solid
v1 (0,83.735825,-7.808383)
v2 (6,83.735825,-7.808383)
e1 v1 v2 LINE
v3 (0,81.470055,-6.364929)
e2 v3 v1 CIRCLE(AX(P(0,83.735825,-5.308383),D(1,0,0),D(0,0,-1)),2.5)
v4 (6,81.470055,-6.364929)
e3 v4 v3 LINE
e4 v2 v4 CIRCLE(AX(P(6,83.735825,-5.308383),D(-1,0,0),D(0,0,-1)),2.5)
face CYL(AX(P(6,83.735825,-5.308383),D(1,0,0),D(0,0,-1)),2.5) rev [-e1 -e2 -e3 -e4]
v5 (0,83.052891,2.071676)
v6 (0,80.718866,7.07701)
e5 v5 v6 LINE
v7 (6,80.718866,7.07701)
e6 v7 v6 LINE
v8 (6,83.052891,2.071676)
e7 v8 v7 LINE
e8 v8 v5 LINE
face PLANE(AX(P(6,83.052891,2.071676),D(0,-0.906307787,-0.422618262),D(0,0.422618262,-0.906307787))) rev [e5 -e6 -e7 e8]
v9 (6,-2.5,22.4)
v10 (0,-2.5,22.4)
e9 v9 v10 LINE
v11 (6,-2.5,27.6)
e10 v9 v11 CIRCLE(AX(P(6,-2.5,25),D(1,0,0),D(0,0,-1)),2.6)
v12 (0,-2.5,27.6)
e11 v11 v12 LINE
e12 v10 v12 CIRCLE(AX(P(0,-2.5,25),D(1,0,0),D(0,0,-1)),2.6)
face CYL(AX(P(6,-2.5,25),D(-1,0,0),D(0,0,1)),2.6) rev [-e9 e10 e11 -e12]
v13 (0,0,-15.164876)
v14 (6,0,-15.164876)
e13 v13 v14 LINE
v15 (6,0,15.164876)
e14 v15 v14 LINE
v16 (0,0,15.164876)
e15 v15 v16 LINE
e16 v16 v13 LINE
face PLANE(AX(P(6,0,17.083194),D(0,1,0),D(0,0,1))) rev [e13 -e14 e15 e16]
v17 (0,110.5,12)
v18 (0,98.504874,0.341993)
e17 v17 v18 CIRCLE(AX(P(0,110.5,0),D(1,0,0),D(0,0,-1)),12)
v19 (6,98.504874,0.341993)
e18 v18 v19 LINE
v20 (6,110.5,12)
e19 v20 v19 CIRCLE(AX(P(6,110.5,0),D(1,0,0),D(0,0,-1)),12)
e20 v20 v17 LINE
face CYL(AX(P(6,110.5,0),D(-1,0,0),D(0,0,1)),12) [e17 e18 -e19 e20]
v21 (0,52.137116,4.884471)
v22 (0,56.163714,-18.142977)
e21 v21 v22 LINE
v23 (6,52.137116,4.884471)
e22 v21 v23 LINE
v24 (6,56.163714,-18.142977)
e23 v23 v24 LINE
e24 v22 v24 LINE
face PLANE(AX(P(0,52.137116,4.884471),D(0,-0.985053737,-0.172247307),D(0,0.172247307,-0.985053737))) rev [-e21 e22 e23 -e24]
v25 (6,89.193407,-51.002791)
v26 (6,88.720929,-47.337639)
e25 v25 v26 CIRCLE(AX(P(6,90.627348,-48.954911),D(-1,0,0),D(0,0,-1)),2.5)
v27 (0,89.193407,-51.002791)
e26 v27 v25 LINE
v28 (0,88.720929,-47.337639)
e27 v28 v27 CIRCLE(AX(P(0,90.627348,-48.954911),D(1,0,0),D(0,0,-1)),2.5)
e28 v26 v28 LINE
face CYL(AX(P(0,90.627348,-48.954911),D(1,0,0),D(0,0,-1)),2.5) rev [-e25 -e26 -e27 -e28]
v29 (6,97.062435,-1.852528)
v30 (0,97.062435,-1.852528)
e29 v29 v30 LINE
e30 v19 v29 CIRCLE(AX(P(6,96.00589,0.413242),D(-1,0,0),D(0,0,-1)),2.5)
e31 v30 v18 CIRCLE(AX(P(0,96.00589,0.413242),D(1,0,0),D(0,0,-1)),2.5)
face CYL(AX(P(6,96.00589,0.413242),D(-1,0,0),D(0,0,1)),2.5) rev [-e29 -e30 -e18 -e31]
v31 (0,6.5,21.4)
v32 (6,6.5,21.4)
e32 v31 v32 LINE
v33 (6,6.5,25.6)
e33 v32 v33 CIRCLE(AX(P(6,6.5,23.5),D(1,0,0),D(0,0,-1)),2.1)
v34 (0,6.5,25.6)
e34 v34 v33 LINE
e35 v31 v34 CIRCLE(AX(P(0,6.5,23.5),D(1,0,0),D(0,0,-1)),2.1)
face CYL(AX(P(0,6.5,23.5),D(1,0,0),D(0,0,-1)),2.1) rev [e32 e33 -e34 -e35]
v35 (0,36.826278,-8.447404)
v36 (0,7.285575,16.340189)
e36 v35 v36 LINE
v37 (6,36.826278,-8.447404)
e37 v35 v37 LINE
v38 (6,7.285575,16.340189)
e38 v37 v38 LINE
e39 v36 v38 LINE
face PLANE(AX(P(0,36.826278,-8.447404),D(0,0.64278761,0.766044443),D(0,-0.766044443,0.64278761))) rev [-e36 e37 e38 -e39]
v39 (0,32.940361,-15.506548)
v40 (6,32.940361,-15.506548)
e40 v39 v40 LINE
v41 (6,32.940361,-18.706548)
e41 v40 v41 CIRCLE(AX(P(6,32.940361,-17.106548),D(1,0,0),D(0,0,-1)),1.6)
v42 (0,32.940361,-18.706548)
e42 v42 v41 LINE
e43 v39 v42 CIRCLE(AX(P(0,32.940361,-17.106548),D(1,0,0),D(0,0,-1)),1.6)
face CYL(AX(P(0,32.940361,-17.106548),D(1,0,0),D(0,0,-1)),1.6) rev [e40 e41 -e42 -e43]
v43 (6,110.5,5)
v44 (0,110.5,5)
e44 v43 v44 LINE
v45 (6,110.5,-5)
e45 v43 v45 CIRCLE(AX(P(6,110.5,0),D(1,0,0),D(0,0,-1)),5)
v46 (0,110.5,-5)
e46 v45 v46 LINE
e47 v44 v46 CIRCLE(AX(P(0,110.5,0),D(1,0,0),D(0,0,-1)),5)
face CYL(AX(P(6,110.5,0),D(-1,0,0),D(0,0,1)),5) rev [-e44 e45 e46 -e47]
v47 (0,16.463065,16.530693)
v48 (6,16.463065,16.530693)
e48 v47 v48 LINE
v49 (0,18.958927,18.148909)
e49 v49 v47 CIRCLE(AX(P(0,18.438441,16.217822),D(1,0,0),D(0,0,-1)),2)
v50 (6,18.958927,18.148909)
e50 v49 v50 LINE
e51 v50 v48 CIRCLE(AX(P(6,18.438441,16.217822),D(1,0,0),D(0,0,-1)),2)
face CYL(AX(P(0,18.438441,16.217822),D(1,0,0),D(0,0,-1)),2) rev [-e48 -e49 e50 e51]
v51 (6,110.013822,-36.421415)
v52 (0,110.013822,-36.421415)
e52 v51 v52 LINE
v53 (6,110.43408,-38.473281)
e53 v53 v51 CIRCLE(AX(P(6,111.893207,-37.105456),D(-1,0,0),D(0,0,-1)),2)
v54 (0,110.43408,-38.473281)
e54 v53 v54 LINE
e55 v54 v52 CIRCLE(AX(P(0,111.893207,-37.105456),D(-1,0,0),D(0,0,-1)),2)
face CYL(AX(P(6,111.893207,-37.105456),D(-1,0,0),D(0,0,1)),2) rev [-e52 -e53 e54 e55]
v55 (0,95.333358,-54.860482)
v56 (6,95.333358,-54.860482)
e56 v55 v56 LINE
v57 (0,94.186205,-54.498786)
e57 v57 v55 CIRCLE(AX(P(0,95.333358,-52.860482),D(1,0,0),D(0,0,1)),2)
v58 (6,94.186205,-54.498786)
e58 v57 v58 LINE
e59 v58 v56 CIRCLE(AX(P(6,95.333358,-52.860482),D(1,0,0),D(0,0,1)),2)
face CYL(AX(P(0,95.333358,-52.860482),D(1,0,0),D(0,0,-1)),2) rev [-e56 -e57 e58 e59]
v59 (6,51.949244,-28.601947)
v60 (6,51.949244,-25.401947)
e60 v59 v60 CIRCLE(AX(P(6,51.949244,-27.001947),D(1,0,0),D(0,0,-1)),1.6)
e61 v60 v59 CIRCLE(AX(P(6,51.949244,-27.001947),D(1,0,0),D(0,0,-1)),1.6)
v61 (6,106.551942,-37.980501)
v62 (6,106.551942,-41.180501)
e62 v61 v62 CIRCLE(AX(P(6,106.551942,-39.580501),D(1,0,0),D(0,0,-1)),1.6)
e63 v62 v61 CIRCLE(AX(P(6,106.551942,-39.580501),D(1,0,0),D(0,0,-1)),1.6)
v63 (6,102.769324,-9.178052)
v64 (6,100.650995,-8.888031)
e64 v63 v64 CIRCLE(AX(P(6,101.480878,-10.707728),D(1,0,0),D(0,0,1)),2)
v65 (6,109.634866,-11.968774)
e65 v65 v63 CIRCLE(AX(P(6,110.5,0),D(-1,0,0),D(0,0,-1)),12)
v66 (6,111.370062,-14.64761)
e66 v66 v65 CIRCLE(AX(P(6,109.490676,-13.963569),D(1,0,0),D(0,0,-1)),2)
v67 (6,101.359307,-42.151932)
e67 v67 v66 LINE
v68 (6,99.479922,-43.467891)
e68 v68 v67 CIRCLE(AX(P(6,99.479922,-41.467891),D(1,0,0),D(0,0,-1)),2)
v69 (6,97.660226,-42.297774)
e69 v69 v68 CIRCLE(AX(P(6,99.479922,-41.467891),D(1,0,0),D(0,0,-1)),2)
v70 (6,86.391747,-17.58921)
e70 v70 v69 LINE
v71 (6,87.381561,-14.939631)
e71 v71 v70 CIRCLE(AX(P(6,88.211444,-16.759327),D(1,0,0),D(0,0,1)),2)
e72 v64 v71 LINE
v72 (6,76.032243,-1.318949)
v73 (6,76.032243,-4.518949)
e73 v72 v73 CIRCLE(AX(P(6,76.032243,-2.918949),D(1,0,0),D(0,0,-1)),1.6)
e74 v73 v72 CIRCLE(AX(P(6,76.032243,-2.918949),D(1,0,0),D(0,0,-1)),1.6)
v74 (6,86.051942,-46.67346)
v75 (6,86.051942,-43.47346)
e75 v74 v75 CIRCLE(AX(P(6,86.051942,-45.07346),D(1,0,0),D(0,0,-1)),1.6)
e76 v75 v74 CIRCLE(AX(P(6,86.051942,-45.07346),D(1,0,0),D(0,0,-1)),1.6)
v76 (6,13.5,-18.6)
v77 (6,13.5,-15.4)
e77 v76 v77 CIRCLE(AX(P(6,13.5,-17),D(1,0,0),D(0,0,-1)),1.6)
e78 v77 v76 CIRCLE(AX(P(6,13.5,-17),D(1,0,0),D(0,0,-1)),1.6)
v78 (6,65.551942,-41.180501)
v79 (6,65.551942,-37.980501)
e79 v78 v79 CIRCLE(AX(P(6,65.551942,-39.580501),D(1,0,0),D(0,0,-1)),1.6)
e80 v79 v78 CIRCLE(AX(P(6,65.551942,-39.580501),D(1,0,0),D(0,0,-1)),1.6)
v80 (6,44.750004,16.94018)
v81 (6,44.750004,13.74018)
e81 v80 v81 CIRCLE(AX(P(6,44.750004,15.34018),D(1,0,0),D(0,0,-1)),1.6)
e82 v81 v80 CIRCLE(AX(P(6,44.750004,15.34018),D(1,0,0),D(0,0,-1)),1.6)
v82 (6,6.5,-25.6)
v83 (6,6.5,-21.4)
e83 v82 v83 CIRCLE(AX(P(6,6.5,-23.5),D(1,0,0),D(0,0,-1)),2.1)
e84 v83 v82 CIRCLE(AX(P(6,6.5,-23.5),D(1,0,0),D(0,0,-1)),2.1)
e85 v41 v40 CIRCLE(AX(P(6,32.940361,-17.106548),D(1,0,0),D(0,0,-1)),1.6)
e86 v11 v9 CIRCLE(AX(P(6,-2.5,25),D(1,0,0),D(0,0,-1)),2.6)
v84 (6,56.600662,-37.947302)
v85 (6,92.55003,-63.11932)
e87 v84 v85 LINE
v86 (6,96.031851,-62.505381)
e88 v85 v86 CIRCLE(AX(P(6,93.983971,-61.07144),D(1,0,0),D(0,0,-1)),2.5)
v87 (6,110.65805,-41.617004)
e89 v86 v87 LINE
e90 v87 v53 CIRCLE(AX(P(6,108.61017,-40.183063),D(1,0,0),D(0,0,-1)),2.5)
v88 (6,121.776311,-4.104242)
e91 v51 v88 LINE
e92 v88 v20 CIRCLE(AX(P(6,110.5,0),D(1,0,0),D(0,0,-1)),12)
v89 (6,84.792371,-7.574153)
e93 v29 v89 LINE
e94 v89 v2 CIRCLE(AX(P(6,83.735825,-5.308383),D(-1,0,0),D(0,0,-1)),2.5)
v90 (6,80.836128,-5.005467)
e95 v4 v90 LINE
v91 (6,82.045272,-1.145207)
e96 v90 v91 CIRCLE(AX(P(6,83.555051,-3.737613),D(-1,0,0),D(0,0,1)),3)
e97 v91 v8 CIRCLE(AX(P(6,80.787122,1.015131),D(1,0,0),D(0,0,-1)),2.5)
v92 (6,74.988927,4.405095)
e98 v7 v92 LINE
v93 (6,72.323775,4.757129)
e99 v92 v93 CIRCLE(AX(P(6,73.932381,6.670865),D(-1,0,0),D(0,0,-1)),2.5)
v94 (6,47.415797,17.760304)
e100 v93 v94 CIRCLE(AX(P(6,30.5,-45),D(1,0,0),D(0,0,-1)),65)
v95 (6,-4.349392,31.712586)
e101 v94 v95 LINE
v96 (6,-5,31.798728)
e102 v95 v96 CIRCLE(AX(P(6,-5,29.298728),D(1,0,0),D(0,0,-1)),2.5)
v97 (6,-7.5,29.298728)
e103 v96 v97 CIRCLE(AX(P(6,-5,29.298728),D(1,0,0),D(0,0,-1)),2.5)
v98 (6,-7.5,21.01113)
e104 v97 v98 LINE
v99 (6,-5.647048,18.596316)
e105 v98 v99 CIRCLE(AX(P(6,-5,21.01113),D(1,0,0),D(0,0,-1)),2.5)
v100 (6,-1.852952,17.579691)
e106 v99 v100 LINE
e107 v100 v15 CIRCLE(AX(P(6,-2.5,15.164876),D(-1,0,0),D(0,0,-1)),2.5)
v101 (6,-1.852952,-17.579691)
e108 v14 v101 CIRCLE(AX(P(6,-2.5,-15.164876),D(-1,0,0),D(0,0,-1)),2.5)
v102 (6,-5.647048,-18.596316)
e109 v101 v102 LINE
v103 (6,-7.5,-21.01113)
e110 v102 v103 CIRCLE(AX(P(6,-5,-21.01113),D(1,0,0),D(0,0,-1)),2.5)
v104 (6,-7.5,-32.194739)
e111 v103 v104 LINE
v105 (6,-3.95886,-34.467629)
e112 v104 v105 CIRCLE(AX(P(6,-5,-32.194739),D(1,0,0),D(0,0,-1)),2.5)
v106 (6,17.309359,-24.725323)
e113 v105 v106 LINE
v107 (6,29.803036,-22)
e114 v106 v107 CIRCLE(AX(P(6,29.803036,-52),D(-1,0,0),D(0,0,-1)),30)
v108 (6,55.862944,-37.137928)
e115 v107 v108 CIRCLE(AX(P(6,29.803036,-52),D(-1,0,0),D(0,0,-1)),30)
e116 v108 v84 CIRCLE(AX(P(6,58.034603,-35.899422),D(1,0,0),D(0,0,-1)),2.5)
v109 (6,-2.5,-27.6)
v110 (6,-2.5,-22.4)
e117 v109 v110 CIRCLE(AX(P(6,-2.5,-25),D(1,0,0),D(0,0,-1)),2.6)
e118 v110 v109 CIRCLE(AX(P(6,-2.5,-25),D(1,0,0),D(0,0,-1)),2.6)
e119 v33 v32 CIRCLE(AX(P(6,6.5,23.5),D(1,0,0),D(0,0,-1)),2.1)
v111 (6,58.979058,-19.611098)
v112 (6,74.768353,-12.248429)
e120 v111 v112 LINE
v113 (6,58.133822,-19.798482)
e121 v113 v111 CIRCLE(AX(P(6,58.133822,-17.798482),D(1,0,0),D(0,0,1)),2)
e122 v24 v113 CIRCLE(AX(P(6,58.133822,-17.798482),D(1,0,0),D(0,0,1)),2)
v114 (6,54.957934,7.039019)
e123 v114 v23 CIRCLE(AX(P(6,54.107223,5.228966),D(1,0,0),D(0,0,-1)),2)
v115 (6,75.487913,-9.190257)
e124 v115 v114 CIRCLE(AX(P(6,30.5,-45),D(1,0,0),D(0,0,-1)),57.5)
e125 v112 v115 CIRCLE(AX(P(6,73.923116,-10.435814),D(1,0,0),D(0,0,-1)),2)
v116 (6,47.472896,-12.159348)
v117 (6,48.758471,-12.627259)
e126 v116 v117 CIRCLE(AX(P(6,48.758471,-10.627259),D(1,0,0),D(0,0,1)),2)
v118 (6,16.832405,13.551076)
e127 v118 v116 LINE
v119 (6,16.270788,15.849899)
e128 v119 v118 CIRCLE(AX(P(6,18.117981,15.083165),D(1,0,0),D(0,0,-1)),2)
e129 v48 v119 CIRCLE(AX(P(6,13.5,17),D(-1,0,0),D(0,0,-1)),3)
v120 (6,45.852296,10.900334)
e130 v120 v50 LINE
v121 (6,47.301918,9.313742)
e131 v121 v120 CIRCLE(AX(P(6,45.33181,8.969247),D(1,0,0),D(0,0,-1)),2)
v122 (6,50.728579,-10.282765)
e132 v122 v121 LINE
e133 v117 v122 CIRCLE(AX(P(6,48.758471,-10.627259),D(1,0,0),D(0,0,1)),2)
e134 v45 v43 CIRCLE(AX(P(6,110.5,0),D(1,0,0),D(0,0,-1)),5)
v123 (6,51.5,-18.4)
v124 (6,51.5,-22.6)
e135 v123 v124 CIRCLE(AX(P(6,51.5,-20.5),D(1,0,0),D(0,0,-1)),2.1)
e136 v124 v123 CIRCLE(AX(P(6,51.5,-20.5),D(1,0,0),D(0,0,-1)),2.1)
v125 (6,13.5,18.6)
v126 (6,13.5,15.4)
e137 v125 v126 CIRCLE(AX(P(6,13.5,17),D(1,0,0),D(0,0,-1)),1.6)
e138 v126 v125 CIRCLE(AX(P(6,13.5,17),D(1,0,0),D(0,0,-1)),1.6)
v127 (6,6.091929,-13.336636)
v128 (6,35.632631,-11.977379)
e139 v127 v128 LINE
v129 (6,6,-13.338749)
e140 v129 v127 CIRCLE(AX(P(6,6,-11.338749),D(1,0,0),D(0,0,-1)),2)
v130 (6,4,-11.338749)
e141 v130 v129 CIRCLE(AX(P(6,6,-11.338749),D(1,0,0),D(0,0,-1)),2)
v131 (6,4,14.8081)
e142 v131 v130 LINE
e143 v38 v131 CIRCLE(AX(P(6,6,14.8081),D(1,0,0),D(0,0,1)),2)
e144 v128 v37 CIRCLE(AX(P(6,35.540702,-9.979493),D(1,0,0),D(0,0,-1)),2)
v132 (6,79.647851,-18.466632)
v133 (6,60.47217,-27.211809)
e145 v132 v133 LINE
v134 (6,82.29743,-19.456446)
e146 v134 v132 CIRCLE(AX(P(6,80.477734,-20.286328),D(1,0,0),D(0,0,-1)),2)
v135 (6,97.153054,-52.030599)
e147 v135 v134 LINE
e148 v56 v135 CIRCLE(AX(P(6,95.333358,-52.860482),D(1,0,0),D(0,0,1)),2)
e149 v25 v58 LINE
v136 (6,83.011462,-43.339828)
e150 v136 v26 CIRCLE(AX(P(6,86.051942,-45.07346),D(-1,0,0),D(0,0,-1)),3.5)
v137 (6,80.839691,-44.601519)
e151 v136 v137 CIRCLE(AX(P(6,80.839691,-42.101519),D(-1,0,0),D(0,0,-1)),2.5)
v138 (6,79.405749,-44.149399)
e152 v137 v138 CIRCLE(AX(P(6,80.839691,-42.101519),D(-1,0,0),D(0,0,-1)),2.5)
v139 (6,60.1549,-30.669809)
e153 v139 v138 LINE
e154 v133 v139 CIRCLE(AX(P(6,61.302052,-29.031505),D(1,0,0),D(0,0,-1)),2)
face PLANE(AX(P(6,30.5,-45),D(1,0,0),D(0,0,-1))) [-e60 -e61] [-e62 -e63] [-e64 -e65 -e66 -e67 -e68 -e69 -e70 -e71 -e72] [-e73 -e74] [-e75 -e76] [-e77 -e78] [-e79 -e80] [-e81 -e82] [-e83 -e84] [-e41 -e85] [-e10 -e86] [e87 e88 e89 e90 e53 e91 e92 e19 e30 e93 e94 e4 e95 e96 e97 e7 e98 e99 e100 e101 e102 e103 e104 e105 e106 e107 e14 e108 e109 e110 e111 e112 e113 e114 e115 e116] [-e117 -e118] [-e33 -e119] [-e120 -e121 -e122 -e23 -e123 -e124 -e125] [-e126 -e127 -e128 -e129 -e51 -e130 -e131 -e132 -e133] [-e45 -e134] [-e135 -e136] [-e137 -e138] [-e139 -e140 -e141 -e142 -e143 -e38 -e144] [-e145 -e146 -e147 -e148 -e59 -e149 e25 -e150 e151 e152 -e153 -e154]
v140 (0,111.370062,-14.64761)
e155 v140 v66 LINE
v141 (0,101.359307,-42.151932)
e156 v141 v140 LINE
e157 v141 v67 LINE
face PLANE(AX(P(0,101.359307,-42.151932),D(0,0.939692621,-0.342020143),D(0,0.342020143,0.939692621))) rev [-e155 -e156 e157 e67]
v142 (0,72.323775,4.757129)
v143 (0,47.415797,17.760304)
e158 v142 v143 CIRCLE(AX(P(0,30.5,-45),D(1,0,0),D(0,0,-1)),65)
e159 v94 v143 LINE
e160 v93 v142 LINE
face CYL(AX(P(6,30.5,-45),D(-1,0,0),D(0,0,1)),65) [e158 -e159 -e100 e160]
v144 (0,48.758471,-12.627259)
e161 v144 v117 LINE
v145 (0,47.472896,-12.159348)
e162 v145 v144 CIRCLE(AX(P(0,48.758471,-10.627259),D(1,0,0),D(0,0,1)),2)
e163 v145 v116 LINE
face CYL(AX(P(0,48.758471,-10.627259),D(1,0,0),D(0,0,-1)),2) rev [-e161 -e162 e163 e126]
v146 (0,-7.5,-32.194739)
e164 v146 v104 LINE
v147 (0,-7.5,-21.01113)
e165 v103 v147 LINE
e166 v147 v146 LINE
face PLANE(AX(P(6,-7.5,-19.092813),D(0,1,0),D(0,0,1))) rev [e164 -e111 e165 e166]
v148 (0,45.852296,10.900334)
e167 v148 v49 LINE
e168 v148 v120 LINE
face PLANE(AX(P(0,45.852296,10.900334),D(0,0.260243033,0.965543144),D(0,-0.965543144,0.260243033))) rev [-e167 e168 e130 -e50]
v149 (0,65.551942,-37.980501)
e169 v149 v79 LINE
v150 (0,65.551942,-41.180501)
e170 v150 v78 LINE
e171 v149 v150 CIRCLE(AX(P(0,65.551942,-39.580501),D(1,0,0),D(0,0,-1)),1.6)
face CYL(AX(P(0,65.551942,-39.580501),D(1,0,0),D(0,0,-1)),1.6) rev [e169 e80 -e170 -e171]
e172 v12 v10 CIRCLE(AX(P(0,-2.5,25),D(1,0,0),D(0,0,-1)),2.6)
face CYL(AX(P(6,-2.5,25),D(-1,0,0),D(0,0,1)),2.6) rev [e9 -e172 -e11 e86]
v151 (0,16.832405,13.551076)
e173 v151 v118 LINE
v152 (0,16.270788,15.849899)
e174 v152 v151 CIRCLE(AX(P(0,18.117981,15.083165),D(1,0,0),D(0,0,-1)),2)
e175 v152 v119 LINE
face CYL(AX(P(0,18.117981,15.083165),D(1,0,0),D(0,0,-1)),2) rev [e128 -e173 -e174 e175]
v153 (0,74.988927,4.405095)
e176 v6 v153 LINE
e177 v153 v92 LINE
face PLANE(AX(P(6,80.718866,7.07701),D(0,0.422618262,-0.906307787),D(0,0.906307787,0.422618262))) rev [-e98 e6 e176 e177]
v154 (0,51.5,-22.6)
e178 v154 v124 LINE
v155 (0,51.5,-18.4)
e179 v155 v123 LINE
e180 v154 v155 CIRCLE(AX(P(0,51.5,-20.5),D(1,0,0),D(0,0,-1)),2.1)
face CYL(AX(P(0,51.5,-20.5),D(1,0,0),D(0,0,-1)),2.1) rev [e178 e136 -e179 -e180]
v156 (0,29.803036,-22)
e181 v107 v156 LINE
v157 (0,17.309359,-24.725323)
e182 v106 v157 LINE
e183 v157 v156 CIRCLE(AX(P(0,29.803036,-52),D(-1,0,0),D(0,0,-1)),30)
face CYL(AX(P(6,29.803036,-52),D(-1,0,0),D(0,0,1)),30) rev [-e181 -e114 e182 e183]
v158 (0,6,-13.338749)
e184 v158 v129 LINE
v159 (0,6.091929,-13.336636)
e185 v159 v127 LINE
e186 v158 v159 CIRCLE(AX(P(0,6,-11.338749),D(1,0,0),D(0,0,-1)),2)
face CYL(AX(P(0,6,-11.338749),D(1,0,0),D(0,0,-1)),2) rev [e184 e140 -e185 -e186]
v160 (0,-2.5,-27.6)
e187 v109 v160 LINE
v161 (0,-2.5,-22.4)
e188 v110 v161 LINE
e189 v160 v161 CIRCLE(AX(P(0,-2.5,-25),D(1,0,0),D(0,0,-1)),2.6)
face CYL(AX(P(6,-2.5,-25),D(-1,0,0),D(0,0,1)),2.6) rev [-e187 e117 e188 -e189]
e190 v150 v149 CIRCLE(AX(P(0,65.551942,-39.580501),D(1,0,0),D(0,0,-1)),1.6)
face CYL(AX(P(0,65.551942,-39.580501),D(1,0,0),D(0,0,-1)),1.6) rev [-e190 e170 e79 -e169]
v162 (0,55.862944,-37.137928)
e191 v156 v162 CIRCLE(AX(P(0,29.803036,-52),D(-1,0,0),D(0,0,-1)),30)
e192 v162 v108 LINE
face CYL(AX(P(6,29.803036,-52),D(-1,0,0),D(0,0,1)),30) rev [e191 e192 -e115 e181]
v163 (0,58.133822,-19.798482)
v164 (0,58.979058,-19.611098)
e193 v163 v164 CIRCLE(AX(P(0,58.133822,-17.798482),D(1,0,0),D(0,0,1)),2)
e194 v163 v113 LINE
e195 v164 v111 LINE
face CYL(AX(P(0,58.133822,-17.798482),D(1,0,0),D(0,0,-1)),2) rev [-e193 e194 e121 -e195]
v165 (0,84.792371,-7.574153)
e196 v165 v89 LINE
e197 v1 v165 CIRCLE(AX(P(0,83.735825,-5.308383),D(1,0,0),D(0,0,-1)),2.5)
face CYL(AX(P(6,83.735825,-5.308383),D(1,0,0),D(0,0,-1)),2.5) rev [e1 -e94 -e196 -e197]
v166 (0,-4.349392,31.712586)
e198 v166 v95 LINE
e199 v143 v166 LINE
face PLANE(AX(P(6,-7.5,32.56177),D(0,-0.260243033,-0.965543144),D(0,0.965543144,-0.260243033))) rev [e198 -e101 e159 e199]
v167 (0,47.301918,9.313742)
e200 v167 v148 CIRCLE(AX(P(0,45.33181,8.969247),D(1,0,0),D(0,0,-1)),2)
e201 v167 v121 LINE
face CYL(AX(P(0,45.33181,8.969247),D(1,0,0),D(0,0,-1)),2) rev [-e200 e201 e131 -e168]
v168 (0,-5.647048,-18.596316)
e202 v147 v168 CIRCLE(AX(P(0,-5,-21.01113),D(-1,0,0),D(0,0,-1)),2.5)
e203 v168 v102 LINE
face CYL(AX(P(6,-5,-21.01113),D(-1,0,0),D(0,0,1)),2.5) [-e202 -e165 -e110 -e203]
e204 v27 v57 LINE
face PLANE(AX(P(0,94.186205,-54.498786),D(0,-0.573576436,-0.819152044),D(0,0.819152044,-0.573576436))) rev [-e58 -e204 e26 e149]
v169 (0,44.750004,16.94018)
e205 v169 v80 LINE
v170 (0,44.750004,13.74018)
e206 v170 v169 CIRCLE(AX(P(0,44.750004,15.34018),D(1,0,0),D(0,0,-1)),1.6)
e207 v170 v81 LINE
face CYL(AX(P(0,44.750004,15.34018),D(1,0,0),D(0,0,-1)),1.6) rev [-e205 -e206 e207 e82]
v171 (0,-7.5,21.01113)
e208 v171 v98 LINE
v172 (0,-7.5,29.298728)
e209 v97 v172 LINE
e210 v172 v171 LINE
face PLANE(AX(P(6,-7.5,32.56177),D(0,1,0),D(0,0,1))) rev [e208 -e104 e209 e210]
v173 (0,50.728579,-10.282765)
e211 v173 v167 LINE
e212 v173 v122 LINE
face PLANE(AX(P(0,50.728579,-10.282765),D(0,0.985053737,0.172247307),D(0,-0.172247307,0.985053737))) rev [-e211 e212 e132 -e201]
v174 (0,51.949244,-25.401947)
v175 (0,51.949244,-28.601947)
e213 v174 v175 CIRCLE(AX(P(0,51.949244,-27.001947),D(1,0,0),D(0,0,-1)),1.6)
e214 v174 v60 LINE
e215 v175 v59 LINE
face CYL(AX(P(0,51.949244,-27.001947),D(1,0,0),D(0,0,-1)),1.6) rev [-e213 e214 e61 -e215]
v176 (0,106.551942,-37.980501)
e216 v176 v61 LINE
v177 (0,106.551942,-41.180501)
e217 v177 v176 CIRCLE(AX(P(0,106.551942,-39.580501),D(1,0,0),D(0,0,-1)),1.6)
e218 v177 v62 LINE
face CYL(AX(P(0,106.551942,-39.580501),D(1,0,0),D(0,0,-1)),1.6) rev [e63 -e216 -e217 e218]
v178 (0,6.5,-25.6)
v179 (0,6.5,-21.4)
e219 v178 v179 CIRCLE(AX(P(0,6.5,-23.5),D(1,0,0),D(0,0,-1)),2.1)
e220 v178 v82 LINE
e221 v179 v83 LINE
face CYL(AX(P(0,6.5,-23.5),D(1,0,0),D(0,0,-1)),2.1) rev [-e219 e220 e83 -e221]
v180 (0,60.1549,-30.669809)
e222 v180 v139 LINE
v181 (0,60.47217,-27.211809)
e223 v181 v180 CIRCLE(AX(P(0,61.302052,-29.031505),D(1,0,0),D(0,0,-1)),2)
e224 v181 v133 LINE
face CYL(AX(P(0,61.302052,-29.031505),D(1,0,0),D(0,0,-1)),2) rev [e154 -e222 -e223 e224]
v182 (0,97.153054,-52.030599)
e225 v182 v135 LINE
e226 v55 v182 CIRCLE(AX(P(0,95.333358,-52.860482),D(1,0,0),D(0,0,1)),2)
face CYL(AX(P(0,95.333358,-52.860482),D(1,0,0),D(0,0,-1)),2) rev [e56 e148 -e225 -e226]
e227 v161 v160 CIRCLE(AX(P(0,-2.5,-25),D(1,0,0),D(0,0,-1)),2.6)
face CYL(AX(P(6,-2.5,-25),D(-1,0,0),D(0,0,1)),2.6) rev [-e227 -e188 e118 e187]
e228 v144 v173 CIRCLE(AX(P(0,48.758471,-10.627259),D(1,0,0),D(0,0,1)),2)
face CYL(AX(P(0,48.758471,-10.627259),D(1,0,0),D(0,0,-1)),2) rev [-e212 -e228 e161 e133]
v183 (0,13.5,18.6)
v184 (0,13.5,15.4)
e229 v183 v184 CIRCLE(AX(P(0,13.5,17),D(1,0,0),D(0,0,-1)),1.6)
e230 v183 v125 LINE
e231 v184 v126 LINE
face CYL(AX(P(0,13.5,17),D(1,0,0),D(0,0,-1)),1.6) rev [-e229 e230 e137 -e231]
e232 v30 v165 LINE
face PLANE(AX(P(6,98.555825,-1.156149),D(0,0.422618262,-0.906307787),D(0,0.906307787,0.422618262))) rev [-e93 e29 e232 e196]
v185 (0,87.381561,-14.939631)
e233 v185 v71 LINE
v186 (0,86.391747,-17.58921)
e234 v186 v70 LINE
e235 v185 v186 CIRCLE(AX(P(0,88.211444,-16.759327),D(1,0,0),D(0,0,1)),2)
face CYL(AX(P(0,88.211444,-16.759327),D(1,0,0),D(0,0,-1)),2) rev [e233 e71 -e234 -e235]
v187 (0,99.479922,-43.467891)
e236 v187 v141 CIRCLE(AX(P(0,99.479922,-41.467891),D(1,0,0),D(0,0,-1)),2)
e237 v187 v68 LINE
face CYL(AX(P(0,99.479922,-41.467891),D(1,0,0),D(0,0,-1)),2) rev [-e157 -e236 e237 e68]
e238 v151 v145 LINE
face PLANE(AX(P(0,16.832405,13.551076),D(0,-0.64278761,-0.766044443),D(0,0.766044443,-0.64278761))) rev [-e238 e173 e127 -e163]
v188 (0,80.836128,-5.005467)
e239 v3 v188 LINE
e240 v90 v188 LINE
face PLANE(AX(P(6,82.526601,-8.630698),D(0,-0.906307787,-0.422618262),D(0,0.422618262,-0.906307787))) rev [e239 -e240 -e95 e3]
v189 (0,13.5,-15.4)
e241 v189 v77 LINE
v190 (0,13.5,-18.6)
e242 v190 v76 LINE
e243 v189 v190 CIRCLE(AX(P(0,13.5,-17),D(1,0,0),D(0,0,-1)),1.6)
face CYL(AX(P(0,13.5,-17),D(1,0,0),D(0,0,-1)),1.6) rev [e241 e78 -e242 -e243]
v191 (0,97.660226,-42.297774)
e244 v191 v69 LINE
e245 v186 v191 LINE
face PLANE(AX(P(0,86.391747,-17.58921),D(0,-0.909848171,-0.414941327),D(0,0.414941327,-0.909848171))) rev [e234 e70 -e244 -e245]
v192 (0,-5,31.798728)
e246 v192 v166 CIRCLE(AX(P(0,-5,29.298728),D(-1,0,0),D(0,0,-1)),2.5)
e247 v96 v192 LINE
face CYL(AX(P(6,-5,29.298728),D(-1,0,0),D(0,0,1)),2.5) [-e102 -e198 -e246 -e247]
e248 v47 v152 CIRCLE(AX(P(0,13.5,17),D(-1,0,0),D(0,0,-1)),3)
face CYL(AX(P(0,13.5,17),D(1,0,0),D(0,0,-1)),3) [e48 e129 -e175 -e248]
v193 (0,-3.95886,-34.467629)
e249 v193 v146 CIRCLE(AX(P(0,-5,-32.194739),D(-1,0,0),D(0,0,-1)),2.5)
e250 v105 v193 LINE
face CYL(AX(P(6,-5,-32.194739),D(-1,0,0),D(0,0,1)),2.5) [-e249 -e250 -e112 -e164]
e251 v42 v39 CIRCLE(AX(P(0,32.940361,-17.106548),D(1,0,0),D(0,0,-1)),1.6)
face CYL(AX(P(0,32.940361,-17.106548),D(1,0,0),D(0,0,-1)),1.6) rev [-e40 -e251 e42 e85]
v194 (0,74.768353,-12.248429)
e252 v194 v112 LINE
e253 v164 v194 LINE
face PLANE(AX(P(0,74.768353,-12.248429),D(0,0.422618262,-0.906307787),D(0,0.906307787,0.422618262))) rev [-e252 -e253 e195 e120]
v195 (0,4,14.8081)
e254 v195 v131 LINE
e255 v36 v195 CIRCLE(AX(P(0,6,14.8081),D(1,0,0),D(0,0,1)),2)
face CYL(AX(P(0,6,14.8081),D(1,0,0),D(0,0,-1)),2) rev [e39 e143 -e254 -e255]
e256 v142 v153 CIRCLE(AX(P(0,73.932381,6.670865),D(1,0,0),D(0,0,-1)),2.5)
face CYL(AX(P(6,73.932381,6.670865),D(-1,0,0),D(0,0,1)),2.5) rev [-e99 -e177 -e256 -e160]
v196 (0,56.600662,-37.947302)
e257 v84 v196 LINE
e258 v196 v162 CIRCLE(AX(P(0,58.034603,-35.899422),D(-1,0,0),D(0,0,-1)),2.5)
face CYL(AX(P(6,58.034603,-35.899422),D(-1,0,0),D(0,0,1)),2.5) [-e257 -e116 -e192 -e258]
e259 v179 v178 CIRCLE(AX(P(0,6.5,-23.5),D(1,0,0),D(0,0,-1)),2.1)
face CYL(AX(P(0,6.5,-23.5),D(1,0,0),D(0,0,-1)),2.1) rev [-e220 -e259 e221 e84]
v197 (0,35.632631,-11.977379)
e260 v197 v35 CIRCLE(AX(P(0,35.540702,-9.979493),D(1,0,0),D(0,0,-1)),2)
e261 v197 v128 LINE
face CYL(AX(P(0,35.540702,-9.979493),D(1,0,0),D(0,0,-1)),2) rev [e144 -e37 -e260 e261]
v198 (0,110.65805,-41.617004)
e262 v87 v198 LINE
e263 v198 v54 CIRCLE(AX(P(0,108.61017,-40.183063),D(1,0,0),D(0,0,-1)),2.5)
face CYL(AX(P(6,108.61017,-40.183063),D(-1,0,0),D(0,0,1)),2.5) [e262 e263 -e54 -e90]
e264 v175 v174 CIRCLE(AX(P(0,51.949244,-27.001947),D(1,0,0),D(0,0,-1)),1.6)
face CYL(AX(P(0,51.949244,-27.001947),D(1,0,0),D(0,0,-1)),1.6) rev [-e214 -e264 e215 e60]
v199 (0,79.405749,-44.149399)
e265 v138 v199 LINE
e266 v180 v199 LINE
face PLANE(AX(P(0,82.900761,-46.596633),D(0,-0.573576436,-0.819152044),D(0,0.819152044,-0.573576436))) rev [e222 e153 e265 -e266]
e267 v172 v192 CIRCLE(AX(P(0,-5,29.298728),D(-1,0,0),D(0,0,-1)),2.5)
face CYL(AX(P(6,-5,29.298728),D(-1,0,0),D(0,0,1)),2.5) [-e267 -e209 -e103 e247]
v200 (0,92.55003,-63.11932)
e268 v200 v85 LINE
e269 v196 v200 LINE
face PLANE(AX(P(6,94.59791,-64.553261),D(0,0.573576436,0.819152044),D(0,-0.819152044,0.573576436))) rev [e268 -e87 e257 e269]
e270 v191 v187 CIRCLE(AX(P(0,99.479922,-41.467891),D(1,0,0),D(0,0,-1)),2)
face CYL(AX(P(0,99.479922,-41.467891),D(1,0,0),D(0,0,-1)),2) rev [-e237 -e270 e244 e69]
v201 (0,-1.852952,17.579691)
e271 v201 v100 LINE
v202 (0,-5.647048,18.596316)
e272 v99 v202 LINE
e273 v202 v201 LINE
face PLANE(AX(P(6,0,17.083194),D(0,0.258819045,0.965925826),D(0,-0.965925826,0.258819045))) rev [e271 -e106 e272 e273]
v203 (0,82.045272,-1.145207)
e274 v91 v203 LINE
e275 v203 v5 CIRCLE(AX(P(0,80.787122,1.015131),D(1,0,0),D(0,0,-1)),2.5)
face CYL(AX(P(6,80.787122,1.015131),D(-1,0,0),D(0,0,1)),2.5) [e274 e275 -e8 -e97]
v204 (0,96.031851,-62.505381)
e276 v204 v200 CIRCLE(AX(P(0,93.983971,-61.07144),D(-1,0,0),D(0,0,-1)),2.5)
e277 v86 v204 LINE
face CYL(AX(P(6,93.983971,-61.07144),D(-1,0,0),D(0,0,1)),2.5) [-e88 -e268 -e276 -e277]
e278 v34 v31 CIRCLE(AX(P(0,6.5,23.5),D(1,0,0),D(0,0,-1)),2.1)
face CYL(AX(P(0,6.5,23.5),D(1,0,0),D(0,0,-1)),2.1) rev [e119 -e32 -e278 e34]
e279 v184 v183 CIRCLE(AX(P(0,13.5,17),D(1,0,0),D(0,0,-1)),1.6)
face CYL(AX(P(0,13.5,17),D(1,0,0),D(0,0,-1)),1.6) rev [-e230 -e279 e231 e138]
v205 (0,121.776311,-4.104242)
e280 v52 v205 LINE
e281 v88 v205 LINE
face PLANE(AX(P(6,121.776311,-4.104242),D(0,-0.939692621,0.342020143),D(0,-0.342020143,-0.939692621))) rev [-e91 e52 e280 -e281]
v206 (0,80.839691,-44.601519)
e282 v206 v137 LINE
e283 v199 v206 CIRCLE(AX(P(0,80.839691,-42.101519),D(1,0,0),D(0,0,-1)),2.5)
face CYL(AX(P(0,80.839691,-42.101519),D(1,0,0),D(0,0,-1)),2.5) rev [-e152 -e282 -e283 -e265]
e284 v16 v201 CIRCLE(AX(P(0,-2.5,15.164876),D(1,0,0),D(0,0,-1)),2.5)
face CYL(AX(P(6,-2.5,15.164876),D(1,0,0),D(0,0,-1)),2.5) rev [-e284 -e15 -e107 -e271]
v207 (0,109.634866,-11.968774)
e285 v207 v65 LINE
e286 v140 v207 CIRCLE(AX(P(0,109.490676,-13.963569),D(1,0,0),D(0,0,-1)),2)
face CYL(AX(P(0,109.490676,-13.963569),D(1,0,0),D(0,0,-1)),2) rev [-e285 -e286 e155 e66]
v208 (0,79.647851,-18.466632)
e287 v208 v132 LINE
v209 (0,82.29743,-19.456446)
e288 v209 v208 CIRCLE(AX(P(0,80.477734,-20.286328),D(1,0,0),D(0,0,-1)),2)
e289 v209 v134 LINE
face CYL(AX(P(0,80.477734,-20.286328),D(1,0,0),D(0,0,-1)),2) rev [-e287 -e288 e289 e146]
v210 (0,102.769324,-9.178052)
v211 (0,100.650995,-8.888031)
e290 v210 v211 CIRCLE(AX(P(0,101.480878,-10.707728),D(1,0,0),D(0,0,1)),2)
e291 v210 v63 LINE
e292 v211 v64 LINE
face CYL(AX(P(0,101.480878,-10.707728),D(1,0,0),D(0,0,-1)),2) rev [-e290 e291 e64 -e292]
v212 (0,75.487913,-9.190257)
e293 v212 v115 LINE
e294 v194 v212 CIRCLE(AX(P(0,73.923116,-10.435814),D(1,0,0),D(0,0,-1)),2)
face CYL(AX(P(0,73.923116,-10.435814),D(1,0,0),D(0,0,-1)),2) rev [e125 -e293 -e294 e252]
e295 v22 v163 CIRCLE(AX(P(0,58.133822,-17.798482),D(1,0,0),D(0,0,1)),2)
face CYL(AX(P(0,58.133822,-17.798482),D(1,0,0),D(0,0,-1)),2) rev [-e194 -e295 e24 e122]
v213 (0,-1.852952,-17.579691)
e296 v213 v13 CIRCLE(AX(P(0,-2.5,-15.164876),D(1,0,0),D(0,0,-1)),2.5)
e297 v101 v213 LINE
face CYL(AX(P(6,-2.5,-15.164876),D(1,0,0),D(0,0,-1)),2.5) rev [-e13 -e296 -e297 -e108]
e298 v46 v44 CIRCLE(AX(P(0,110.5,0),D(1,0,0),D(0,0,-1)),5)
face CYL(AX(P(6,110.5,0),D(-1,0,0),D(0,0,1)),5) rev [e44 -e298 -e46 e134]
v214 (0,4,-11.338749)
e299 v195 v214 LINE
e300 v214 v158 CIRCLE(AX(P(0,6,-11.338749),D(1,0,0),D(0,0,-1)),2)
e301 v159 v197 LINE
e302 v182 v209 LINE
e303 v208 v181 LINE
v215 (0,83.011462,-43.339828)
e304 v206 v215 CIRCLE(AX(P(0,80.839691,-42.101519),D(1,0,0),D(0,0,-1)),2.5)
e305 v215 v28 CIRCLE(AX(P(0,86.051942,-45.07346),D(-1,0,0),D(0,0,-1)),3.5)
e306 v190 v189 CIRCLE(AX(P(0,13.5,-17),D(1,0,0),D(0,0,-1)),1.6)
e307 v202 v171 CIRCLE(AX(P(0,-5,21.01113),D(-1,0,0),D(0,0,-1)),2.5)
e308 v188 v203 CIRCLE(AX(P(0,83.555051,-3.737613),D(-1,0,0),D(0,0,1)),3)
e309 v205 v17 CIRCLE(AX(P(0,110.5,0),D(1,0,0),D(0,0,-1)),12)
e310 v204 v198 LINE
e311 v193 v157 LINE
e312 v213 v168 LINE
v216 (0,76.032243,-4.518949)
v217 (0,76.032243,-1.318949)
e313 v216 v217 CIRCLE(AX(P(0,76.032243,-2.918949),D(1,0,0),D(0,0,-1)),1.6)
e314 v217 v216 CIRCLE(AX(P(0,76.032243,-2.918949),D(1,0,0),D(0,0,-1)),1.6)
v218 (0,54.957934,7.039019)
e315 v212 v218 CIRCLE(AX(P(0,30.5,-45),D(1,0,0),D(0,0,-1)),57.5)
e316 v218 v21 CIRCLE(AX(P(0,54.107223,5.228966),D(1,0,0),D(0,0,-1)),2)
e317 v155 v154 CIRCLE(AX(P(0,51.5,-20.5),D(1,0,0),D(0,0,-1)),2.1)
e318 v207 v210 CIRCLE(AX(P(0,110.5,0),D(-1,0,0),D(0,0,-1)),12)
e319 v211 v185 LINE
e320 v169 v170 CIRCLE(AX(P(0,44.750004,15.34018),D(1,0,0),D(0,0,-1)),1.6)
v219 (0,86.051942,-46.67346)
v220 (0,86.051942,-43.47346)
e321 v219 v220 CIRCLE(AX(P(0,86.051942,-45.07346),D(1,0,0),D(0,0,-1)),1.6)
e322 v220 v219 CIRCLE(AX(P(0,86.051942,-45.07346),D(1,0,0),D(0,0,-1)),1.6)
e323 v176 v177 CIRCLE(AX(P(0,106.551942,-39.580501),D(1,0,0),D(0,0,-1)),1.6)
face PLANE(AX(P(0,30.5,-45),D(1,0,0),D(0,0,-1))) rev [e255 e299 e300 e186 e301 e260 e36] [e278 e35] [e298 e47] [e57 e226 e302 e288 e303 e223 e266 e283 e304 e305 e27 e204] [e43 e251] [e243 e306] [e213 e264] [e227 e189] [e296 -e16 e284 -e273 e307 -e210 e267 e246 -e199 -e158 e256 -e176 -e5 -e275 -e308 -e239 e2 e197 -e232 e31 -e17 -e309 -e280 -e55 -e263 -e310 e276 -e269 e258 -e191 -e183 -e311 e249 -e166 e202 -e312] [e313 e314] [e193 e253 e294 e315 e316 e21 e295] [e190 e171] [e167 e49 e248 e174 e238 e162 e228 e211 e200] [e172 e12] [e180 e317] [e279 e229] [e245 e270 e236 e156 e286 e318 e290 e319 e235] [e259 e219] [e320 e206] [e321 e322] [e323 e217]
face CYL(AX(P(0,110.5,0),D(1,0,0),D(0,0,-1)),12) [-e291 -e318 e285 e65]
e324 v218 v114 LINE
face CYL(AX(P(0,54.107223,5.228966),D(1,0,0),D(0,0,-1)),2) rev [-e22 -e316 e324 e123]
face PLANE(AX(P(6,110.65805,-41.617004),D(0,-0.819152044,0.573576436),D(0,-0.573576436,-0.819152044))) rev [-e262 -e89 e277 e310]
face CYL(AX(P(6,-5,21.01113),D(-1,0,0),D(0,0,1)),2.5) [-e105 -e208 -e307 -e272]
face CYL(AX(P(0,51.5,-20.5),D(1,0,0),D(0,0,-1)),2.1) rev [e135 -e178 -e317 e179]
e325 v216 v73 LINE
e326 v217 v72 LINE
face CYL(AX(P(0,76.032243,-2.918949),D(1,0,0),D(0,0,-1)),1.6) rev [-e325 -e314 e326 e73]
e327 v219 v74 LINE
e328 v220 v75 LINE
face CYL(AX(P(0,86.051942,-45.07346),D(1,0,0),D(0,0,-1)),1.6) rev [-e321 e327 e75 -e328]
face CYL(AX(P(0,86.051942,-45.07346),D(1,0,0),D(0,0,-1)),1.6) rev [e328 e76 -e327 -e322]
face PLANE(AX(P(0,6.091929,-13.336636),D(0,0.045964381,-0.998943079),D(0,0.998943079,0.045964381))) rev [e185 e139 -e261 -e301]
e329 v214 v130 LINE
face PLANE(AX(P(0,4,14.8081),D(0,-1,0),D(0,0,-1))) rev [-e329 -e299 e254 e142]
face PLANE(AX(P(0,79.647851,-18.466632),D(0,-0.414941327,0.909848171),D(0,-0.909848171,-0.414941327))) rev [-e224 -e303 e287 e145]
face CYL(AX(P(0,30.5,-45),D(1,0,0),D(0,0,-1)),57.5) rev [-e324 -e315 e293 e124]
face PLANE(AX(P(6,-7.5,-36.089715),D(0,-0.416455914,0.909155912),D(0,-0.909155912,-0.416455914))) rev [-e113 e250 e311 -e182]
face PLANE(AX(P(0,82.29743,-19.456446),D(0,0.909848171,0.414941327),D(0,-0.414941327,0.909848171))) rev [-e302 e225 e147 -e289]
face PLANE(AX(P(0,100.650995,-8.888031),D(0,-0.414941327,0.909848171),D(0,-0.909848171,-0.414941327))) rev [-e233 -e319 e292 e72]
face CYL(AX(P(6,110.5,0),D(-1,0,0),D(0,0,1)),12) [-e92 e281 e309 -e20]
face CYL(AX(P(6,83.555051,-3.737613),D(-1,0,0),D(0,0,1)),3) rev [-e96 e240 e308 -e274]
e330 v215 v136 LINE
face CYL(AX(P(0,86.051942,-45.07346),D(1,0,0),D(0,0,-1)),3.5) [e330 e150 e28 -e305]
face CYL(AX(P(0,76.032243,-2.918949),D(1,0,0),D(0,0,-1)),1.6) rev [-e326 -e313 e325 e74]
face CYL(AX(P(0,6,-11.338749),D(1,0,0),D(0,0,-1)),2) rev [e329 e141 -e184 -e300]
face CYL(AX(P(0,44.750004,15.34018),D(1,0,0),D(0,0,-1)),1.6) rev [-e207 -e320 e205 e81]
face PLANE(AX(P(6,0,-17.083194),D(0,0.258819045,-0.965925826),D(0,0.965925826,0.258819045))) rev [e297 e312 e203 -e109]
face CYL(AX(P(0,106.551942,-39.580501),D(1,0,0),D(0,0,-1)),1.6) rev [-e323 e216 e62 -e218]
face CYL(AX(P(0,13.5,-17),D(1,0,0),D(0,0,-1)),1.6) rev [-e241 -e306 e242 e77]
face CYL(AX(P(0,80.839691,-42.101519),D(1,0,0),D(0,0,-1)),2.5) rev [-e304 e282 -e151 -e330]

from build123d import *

# Parameters (mm, degrees)
SKETCH_1_R          = 5
SKETCH_1_R_2        = 2.6
EXTRUDE_1_DEPTH     = 6
SKETCH_2_R          = 1.6
SKETCH_2_R_2        = 2.1
CUT_EXTRUDE_1_DEPTH = 139.597884305
CUT_EXTRUDE_2_DEPTH = 139.597884305
FILLET_R2_5_1_R     = 2.5


with BuildPart() as part:
    # 草图1 → 凸台-拉伸1 (new body)
    with BuildSketch(Plane(origin=(0, 0, 0), x_dir=(0, 0, -1), z_dir=(1, 0, 0))):
        with BuildLine():
            Line((-17.083193756, 0), (17.083193756, 0))
            Line((17.083193756, 0), (19.092812699, -7.5))
            Line((19.092812699, -7.5), (36.089714585, -7.5))
            Line((36.089714585, -7.5), (24.725322655, 17.309358564))
            ThreePointArc((24.725322655, 17.309358564), (23.529105799, 39.258626053), (37.618636127, 56.131278873))
            Line((37.618636127, 56.131278873), (64.553261218, 94.597910009))
            Line((64.553261218, 94.597910009), (41.617003978, 110.658050227))
            ThreePointArc((41.617003978, 110.658050227), (40.005403895, 111.103849583), (38.473281109, 110.434079727))
            ThreePointArc((38.473281109, 110.434079727), (37.50675935, 109.933882183), (36.421415399, 110.013822175))
            Line((36.421415399, 110.013822175), (4.10424172, 121.776311449))
            ThreePointArc((4.10424172, 121.776311449), (-11.904439355, 112.011397909), (1.156148672, 98.55582484))
            Line((1.156148672, 98.55582484), (8.630698442, 82.526601129))
            Line((8.630698442, 82.526601129), (5.005467294, 80.836128082))
            ThreePointArc((5.005467294, 80.836128082), (2.840887568, 80.692205939), (1.145207204, 82.045271746))
            ThreePointArc((1.145207204, 82.045271746), (-0.267859766, 83.172826585), (-2.071676205, 83.052891466))
            Line((-2.071676205, 83.052891466), (-7.077009672, 80.718866138))
            Line((-7.077009672, 80.718866138), (-3.722354698, 73.52478533))
            ThreePointArc((-3.722354698, 73.52478533), (-12.249590693, 61.281233983), (-17.760304381, 47.415797172))
            Line((-17.760304381, 47.415797172), (-32.561769984, -7.5))
            Line((-32.561769984, -7.5), (-19.092812699, -7.5))
            Line((-19.092812699, -7.5), (-17.083193756, 0))
        make_face()
        with Locations((0, 110.5)):
            Circle(SKETCH_1_R, mode=Mode.SUBTRACT)
        with Locations((-25, -2.5)):
            Circle(SKETCH_1_R_2, mode=Mode.SUBTRACT)
        with Locations((25, -2.5)):
            Circle(SKETCH_1_R_2, mode=Mode.SUBTRACT)
    extrude(amount=EXTRUDE_1_DEPTH)

    # 草图2 → 切除-拉伸1 (cut, through all)
    with BuildSketch(Plane(origin=(6, 0, 0), x_dir=(0, 0, -1), z_dir=(1, 0, 0))):
        with Locations((-17, 13.5)):
            Circle(SKETCH_2_R)
        with Locations((17, 13.5)):
            Circle(SKETCH_2_R)
        with Locations((39.580501258, 106.551942354)):
            Circle(SKETCH_2_R)
        with Locations((45.073459702, 86.051942354)):
            Circle(SKETCH_2_R)
        with Locations((39.580501258, 65.551942354)):
            Circle(SKETCH_2_R)
        with Locations((27.001946929, 51.949244407)):
            Circle(SKETCH_2_R)
        with Locations((17.106548453, 32.940360797)):
            Circle(SKETCH_2_R)
        with Locations((2.918948689, 76.032242648)):
            Circle(SKETCH_2_R)
        with Locations((-15.340180452, 44.750004318)):
            Circle(SKETCH_2_R)
        with Locations((-23.5, 6.5)):
            Circle(SKETCH_2_R_2)
        with Locations((23.5, 6.5)):
            Circle(SKETCH_2_R_2)
        with Locations((20.5, 51.5)):
            Circle(SKETCH_2_R_2)
    extrude(amount=-CUT_EXTRUDE_1_DEPTH, mode=Mode.SUBTRACT)

    # 草图3 → 切除-拉伸2 (cut, through all)
    with BuildSketch(Plane(origin=(6, 0, 0), x_dir=(0, 0, -1), z_dir=(1, 0, 0))):
        with BuildLine():
            Line((12.248429119, 74.768352656), (19.611098021, 58.979058243))
            ThreePointArc((19.611098021, 58.979058243), (19.571846918, 57.209063128), (18.142977061, 56.163714245))
            Line((18.142977061, 56.163714245), (-4.884471281, 52.137115682))
            ThreePointArc((-4.884471281, 52.137115682), (-6.818374298, 52.893229365), (-7.039018719, 54.957933901))
            ThreePointArc((-7.039018719, 54.957933901), (-0.107884381, 66.158502025), (9.190257276, 75.487913111))
            ThreePointArc((9.190257276, 75.487913111), (10.893886548, 75.869951802), (12.248429119, 74.768352656))
        make_face()
        with BuildLine():
            Line((8.888031445, 100.650995125), (14.939630847, 87.381560906))
            ThreePointArc((14.939630847, 87.381560906), (16.059423219, 86.337908285), (17.589209845, 86.391747219))
            Line((17.589209845, 86.391747219), (42.297774007, 97.660225561))
            ThreePointArc((42.297774007, 97.660225561), (43.466338702, 99.558713974), (42.151931639, 101.359307145))
            Line((42.151931639, 101.359307145), (14.64760953, 111.370061707))
            ThreePointArc((14.64760953, 111.370061707), (12.876257738, 111.169293065), (11.968773637, 109.634865542))
            ThreePointArc((11.968773637, 109.634865542), (11.116698186, 105.981258866), (9.17805239, 102.769323811))
            ThreePointArc((9.17805239, 102.769323811), (8.726212744, 101.752167532), (8.888031445, 100.650995125))
        make_face()
        with BuildLine():
            Line((19.456445818, 82.297430448), (52.030599002, 97.153054484))
            ThreePointArc((52.030599002, 97.153054484), (54.397990964, 96.612445758), (54.498785746, 94.186205269))
            Line((54.498785746, 94.186205269), (48.555557448, 85.698395622))
            ThreePointArc((48.555557448, 85.698395622), (42.206427547, 88.059459881), (46.596632527, 82.900760901))
            Line((46.596632527, 82.900760901), (30.669808994, 60.154899618))
            ThreePointArc((30.669808994, 60.154899618), (28.848773175, 59.310417706), (27.211808562, 60.472169836))
            Line((27.211808562, 60.472169836), (18.466632131, 79.647851451))
            ThreePointArc((18.466632131, 79.647851451), (18.412793197, 81.177638076), (19.456445818, 82.297430448))
        make_face()
        with BuildLine():
            Line((10.282764815, 50.728578892), (-9.313741825, 47.301917619))
            ThreePointArc((-9.313741825, 47.301917619), (-10.318290453, 46.808320331), (-10.9003335, 45.852296211))
            Line((-10.9003335, 45.852296211), (-18.148908609, 18.958926922))
            ThreePointArc((-18.148908609, 18.958926922), (-17.895966668, 17.350400621), (-16.530693392, 16.463064513))
            ThreePointArc((-16.530693392, 16.463064513), (-16.184608866, 16.387063785), (-15.849899102, 16.270788322))
            ThreePointArc((-15.849899102, 16.270788322), (-14.608512176, 16.17512065), (-13.551076283, 16.832405317))
            Line((-13.551076283, 16.832405317), (12.159348315, 47.472896199))
            ThreePointArc((12.159348315, 47.472896199), (12.36002095, 49.757239414), (10.282764815, 50.728578892))
        make_face()
        with BuildLine():
            Line((-14.808099853, 4), (11.338749368, 4))
            ThreePointArc((11.338749368, 4), (12.78509952, 4.618670482), (13.336635527, 6.091928763))
            Line((13.336635527, 6.091928763), (11.977378786, 35.632631153))
            ThreePointArc((11.977378786, 35.632631153), (10.620148339, 37.435315876), (8.447403741, 36.82627761))
            Line((8.447403741, 36.82627761), (-16.340188739, 7.285575219))
            ThreePointArc((-16.340188739, 7.285575219), (-16.620715427, 5.154763477), (-14.808099853, 4))
        make_face()
    extrude(amount=-CUT_EXTRUDE_2_DEPTH, mode=Mode.SUBTRACT)

    # R2.5 圆角1
    fillet_r2_5_1_edges = [part.edges().sort_by_distance(p)[0] for p in [
        (3, 85.698395622, -48.555557448),
        (3, 82.900760901, -46.596632527),
        (3, -7.5, 19.092812699),
        (3, -7.5, 32.561769984),
        (3, 73.52478533, 3.722354698),
        (3, 82.526601129, -8.630698442),
        (3, 98.55582484, -1.156148672),
        (3, 94.597910009, -64.553261218),
        (3, 56.131278873, -37.618636127),
        (3, -7.5, -36.089714585),
        (3, -7.5, -19.092812699),
        (3, 0, -17.083193756),
        (3, 0, 17.083193756),
    ]]
    fillet(fillet_r2_5_1_edges, radius=FILLET_R2_5_1_R)


solid = part.part
